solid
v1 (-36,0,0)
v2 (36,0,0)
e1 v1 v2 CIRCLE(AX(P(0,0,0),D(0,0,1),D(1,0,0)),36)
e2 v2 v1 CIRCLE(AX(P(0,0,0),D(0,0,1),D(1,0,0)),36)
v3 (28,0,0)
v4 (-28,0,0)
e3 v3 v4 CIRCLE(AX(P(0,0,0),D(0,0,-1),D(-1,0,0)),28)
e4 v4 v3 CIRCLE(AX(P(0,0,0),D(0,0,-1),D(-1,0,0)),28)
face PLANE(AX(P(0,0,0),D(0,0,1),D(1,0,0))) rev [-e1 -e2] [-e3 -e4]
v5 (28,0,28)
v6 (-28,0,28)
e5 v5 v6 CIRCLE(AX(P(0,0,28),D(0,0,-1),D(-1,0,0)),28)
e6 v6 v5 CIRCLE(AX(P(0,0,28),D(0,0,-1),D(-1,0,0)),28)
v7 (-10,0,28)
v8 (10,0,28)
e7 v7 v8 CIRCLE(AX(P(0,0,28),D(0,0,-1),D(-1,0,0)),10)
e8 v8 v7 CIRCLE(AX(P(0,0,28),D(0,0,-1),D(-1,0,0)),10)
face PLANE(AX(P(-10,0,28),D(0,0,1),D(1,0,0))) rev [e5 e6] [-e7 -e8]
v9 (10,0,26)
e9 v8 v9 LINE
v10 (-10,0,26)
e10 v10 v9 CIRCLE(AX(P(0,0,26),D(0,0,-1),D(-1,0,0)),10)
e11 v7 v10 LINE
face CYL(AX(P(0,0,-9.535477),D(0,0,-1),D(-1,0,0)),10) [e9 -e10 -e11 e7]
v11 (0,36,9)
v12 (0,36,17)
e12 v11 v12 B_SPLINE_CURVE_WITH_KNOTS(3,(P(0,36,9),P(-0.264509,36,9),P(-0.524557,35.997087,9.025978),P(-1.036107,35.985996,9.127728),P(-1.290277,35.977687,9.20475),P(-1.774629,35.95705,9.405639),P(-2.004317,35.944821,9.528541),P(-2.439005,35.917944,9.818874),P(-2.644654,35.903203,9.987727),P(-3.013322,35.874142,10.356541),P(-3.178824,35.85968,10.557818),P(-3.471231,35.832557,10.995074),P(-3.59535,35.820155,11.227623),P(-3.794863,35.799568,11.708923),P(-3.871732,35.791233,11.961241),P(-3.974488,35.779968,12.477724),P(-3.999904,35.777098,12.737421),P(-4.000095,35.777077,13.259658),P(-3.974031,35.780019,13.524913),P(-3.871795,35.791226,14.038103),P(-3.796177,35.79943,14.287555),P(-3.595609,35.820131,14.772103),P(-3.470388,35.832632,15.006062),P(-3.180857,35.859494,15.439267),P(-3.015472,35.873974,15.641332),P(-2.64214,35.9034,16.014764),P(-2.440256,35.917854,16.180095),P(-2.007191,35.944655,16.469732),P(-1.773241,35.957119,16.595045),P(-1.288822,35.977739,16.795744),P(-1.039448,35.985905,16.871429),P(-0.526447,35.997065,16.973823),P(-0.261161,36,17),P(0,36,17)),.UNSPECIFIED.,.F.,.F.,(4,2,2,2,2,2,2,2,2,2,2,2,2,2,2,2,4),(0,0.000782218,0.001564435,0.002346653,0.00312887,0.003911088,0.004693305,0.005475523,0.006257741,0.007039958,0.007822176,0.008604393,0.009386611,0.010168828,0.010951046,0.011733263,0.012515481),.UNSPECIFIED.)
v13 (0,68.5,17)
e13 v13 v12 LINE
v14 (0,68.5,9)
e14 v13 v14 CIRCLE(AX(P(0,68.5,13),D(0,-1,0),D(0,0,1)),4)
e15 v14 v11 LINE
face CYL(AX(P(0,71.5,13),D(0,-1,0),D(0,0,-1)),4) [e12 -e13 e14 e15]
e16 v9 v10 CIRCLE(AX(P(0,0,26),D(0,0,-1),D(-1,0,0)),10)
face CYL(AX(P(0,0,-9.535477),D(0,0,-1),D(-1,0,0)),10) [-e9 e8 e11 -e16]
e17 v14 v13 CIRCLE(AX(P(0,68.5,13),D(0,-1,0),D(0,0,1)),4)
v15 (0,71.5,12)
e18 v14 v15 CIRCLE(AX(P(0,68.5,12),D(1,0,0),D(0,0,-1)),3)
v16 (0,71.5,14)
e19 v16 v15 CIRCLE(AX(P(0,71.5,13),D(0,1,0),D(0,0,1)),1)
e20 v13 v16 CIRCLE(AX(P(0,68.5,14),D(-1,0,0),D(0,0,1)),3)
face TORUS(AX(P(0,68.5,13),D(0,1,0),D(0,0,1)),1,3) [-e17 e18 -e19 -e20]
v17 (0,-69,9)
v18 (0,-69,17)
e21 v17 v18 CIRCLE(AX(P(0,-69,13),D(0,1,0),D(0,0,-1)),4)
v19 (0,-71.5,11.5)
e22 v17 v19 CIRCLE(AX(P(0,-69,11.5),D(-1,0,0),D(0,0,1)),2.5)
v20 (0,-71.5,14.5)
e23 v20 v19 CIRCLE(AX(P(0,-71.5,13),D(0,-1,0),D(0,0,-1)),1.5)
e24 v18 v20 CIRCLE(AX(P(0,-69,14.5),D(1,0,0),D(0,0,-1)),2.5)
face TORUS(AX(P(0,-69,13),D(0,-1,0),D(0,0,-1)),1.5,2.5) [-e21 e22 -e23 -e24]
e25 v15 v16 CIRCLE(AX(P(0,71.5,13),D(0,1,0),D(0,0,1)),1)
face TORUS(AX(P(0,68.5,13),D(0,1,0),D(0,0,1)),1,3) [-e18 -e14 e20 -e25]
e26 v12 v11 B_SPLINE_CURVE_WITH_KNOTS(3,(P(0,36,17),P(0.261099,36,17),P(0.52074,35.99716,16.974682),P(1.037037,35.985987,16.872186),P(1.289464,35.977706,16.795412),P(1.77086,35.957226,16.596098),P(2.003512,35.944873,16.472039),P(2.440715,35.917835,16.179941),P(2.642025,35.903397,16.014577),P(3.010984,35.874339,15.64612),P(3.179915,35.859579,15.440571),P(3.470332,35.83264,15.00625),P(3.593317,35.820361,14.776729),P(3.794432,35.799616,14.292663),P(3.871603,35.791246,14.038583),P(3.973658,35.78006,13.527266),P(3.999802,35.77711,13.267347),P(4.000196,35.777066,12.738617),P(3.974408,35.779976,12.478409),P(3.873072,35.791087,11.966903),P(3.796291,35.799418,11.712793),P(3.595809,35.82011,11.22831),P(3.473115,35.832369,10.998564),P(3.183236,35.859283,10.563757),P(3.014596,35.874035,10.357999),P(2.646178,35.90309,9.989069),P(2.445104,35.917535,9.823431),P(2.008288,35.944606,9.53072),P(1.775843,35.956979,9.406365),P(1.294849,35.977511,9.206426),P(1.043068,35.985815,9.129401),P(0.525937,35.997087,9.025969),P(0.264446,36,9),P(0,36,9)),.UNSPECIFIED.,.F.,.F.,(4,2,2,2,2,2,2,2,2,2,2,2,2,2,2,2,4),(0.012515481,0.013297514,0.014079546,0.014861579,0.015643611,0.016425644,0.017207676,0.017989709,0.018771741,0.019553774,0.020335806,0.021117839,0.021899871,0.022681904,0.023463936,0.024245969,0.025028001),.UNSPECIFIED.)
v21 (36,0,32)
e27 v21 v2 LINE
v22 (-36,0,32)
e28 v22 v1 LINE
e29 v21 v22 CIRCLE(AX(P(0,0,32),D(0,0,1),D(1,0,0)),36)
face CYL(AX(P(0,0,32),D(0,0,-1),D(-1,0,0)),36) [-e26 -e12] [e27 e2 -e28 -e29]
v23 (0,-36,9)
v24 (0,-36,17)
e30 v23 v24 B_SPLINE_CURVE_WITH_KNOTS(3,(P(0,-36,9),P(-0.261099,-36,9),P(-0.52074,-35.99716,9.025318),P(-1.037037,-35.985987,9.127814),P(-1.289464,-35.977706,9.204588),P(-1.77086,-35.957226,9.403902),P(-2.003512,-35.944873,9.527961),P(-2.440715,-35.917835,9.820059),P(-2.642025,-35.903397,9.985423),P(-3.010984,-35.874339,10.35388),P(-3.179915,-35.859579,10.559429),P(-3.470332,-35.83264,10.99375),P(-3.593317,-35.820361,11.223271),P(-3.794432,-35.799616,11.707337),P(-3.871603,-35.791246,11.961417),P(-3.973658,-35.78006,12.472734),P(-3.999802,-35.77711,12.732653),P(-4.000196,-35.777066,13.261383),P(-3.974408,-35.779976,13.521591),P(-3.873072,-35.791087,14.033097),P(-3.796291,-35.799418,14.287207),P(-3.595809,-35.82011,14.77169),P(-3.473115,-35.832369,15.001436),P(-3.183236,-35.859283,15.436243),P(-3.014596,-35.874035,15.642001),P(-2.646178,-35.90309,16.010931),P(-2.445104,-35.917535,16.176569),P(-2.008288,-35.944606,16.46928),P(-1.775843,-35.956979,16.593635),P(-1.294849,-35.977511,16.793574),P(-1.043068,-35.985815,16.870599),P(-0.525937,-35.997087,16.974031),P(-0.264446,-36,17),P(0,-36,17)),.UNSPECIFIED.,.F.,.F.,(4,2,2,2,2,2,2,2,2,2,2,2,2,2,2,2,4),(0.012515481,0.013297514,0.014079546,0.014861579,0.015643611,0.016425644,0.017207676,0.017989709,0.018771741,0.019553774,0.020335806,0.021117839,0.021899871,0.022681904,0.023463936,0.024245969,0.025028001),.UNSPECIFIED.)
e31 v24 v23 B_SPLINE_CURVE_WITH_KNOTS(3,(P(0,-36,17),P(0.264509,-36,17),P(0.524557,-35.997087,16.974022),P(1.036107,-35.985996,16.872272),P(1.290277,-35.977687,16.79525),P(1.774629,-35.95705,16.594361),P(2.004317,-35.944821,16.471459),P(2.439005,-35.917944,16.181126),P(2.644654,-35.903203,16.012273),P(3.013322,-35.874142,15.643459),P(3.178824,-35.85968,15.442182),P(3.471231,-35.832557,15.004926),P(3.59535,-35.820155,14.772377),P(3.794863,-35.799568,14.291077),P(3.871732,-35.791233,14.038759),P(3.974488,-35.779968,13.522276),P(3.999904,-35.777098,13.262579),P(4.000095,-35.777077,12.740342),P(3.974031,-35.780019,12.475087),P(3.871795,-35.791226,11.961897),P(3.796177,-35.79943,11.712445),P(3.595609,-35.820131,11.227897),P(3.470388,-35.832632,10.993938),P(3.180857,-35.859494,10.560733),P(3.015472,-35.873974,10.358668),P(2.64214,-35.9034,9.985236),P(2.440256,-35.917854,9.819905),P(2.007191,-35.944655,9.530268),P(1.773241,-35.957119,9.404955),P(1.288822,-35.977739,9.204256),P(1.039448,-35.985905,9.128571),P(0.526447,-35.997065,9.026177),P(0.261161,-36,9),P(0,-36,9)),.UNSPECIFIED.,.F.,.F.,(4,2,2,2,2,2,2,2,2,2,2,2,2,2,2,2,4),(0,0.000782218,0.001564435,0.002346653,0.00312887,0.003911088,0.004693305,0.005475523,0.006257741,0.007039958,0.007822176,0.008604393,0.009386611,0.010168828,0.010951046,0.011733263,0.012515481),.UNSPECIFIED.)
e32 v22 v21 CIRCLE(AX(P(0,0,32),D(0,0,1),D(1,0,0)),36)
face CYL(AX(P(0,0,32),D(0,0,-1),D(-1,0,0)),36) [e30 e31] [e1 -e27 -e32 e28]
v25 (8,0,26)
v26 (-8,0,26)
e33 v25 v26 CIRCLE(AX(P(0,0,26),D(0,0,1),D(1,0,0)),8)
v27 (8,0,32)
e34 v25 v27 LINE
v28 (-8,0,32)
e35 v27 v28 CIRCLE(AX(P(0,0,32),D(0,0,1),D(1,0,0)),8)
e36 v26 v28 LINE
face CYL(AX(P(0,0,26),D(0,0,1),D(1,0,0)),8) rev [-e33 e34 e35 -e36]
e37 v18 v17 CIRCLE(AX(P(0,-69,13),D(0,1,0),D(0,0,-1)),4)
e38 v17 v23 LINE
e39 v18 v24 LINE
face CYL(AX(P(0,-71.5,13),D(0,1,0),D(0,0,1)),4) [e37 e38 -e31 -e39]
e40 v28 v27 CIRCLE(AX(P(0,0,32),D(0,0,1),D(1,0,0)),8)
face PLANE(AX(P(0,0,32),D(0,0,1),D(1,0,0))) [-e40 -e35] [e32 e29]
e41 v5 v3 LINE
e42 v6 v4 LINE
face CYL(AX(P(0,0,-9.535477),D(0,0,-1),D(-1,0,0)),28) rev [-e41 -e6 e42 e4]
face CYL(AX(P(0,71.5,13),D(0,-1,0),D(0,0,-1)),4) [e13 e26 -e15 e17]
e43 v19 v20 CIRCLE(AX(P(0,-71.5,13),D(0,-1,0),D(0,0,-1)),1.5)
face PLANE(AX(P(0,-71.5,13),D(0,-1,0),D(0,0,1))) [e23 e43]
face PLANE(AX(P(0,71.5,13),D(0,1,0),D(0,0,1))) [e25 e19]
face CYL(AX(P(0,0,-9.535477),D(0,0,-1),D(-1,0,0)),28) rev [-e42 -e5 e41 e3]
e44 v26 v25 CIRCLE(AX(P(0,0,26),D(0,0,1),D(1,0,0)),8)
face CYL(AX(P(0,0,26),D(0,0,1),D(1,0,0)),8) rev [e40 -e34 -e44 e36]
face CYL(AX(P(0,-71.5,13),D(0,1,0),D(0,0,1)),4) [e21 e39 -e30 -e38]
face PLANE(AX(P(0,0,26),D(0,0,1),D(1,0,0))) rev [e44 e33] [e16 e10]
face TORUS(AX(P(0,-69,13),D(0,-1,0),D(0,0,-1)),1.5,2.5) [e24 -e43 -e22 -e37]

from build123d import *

# Parameters (mm, degrees)
HUB_PROFILE_SKETCH_R       = 36
HUB_72X32_DEPTH            = 32
HANDLE_START               = 35.5
HANDLE_PIN_SKETCH_8_R      = 4
HANDLE_PIN_8_DEPTH         = 36
PIN_END_FILLET_R3_R        = 3
FACE_RECESS_SKETCH_16_R    = 8
FACE_RECESS_16X6_DEPTH     = 6
MIRRORED_PIN_FILLET_R2_5_R = 2.5


with BuildPart() as part:
    # Hub Profile Sketch → Hub Ø72x32 (new body)
    with BuildSketch(Plane.XY):
        Circle(HUB_PROFILE_SKETCH_R)
    extrude(amount=HUB_72X32_DEPTH)

    # Handle Pin Sketch Ø8 → Handle Pin Ø8 (add)
    with BuildSketch(Plane(origin=(0, 0, 0), x_dir=(1, 0, 0), z_dir=(0, 1, 0)).offset(HANDLE_START)):
        with Locations(Location((0, -13, 0), (0, 0, 90))):
            Circle(HANDLE_PIN_SKETCH_8_R)
    handle_pin_8 = extrude(amount=HANDLE_PIN_8_DEPTH)

    # Pin End Fillet R3
    pin_end_fillet_r3_edges = [part.edges().sort_by_distance(p)[0] for p in [
        (0, 71.5, 17),
    ]]
    fillet(pin_end_fillet_r3_edges, radius=PIN_END_FILLET_R3_R)

    # Handle Pin Mirror: Handle Pin Ø8 across plane
    add(handle_pin_8.mirror(Plane.ZX))

    # Revolved Cut Sketch → Revolved Cut (revolve, cut)
    with BuildSketch(Plane(origin=(0, 0, 0), x_dir=(1, 0, 0), z_dir=(0, 1, 0))):
        Polygon((0, -26), (-10, -26), (-10, -28), (-28, -28), (-28, 0), (0, 0), align=None)
    revolve(axis=Axis((0, 0, -9.53547678), (0, 0, 1)), mode=Mode.SUBTRACT)

    # Face Recess Sketch Ø16 → Face Recess Ø16x6 (cut)
    with BuildSketch(Plane.XY.offset(32)):
        Circle(FACE_RECESS_SKETCH_16_R)
    extrude(amount=-FACE_RECESS_16X6_DEPTH, mode=Mode.SUBTRACT)

    # Mirrored Pin Fillet R2.5
    mirrored_pin_fillet_r2_5_edges = [part.edges().sort_by_distance(p)[0] for p in [
        (0, -71.5, 17),
    ]]
    fillet(mirrored_pin_fillet_r2_5_edges, radius=MIRRORED_PIN_FILLET_R2_5_R)


solid = part.part
